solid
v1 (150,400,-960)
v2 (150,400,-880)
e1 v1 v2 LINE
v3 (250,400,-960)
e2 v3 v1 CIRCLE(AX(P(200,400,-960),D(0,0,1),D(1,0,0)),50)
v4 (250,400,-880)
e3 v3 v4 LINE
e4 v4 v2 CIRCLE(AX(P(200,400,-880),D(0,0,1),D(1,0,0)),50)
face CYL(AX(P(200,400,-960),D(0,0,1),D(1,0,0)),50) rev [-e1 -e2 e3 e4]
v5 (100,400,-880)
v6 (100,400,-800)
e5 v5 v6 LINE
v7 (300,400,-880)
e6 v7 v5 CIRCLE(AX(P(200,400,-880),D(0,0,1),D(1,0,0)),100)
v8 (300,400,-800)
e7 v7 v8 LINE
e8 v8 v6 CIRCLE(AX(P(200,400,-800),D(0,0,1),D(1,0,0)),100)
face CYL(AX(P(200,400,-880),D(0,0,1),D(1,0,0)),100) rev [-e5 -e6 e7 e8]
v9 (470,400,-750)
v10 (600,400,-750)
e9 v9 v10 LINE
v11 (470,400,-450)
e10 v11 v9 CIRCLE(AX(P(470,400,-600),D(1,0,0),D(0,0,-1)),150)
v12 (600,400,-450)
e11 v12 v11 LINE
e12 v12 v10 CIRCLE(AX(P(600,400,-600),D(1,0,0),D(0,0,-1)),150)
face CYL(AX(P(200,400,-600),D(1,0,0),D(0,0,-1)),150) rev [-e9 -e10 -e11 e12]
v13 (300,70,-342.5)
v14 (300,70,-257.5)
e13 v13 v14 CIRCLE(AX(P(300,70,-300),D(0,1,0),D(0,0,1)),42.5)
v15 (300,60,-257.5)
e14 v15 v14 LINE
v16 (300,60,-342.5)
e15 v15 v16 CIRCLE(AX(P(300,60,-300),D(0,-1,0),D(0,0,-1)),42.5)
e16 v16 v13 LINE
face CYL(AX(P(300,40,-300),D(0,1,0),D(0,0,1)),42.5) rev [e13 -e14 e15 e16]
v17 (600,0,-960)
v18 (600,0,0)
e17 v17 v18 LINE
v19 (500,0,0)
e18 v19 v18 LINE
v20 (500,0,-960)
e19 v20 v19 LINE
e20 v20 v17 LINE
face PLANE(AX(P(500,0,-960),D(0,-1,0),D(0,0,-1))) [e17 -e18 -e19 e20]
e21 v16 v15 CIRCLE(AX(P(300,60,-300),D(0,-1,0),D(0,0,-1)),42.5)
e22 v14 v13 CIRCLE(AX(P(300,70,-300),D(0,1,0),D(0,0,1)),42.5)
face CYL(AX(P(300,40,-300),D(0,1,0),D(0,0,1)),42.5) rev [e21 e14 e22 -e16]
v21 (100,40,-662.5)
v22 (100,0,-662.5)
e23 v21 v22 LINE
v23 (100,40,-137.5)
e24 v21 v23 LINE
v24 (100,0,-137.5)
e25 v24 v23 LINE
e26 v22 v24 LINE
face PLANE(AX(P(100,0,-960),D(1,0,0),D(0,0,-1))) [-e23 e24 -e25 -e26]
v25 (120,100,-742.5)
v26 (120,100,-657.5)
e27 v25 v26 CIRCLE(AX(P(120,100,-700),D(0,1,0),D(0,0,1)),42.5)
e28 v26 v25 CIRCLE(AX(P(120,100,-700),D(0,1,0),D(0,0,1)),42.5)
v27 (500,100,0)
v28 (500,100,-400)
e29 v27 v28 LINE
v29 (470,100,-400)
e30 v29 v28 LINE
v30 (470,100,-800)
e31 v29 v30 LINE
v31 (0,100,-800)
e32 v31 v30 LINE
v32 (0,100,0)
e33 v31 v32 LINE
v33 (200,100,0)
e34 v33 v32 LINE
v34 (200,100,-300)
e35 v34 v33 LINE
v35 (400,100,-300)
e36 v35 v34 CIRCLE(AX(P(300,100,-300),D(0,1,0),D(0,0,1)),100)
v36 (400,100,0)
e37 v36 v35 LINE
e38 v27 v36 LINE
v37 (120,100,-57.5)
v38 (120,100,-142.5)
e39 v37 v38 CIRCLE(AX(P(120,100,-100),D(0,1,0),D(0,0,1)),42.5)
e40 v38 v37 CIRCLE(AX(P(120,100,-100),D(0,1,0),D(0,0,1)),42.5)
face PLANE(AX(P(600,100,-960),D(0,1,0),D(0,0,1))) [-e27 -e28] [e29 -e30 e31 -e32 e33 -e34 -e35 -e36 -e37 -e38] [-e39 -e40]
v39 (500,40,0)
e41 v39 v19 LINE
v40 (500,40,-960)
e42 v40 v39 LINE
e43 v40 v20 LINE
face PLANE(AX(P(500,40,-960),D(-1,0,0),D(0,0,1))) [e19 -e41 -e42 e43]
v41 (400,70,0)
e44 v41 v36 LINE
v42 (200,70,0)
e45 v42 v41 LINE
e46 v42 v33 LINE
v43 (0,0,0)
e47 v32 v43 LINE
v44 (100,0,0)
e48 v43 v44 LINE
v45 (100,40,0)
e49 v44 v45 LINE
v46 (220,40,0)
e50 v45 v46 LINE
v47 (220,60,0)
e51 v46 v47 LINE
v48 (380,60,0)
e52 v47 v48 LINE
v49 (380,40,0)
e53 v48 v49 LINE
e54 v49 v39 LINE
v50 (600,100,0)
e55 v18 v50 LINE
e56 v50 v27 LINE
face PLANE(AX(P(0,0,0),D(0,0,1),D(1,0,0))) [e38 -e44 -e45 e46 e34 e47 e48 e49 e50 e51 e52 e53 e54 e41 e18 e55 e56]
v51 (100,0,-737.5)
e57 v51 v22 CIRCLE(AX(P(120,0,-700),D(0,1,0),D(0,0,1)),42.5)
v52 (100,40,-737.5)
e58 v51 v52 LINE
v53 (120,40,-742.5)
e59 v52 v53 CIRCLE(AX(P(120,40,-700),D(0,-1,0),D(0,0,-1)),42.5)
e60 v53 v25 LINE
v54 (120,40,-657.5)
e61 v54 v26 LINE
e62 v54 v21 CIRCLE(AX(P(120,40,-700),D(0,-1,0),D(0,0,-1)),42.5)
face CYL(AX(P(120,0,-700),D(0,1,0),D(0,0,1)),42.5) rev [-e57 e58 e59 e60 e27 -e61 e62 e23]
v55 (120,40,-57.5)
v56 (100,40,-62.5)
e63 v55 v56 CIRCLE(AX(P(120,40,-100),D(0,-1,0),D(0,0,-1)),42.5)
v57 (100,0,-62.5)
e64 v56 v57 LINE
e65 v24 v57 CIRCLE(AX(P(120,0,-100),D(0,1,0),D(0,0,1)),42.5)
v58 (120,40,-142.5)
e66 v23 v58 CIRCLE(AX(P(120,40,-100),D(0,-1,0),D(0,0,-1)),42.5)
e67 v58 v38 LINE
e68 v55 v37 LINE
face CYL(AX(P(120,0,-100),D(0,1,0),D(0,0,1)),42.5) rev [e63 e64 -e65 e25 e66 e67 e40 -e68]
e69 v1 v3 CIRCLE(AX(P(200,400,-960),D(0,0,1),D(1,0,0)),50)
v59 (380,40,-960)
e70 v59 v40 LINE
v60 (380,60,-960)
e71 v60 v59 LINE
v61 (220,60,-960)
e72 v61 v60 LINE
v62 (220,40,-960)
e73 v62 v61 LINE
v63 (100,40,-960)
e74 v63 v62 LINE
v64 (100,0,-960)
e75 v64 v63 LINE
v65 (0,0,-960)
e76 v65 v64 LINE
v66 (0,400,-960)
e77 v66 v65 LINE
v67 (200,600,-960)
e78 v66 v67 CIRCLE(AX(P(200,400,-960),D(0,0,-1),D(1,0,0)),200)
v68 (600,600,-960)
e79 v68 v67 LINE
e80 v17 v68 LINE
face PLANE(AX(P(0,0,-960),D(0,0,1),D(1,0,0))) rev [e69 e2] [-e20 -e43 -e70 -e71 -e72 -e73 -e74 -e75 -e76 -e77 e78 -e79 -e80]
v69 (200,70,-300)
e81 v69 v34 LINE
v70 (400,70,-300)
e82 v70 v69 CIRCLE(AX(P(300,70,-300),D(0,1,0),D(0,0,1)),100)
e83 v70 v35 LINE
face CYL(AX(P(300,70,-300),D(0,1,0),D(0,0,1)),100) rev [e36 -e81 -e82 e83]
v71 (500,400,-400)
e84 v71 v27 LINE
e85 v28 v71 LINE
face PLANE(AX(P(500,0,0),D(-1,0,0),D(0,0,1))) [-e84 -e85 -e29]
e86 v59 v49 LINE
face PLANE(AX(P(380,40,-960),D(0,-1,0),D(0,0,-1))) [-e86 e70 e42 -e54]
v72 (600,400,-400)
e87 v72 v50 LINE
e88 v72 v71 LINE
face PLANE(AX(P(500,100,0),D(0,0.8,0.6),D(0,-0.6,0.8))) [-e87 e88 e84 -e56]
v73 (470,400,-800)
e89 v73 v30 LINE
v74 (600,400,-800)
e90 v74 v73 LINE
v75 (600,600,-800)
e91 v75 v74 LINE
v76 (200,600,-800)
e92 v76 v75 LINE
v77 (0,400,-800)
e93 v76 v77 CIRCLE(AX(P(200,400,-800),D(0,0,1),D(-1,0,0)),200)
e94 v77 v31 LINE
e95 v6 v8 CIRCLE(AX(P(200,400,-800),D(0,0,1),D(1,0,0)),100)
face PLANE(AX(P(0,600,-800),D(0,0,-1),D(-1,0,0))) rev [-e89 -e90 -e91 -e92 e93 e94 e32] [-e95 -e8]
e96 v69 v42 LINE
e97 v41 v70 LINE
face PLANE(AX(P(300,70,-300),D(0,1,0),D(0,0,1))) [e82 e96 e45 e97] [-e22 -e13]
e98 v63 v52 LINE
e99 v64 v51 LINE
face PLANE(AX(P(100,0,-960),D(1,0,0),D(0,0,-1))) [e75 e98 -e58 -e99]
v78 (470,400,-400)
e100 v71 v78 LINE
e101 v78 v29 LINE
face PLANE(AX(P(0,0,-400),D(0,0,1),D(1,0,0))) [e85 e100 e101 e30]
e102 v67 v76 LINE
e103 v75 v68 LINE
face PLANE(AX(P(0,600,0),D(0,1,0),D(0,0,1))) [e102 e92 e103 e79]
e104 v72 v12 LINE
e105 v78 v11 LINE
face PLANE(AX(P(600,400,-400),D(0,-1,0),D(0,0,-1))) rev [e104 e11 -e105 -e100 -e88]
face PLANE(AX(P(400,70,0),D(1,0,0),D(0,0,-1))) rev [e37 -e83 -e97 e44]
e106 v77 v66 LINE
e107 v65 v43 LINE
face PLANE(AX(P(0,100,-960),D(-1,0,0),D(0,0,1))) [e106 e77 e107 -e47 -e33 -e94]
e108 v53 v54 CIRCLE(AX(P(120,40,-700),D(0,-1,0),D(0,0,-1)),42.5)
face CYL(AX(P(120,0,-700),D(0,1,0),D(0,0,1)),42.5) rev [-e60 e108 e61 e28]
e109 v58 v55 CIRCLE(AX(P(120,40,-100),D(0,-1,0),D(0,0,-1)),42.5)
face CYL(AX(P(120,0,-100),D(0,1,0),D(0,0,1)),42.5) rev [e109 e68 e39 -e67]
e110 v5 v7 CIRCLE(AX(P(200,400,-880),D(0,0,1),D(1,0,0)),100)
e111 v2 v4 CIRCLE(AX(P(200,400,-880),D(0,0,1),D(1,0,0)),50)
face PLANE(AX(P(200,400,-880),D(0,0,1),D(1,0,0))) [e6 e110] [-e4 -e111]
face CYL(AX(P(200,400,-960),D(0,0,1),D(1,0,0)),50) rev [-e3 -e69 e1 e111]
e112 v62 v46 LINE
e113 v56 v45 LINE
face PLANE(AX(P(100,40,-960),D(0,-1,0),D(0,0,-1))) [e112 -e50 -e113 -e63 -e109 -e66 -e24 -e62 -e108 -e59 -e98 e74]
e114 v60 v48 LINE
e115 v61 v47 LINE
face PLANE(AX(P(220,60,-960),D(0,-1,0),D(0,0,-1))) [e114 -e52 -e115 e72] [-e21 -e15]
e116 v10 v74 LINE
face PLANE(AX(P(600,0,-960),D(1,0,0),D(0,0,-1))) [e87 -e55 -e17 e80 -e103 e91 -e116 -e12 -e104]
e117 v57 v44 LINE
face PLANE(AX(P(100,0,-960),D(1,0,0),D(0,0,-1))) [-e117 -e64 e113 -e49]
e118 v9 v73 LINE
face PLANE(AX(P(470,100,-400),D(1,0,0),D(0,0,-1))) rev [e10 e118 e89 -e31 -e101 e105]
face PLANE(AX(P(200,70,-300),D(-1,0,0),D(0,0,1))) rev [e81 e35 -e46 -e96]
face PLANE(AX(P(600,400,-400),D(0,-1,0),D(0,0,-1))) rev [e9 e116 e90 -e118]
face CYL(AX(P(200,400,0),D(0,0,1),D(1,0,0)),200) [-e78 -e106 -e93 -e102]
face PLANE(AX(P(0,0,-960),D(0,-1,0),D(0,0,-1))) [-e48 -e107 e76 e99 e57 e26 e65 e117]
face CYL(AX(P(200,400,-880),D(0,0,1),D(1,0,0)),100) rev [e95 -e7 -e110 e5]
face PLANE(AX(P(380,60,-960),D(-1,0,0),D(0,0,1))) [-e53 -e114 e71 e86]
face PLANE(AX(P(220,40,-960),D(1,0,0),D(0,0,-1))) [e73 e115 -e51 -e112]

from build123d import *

# Parameters (mm, degrees)
BASE_PLATE_DEPTH            = 960
UPRIGHT_SKETCH_W            = 600
UPRIGHT_SKETCH_H            = 160
UPRIGHT_DEPTH               = 500
UPRIGHT_TOP_ROUND_R200_R    = 200
BORE_COUNTERBORE_SKETCH_R   = 100
BORE_COUNTERBORE_200_DEPTH  = 80
THROUGH_BORE_SKETCH_R       = 50
THROUGH_BORE_100_DEPTH      = 1223.456543195
MOUNTING_HOLES_SKETCH_R     = 42.5
MOUNTING_HOLES_2X_85_DEPTH  = 1238.578280352
BASE_POCKET_30_DEEP_DEPTH   = 30
POCKET_HOLE_SKETCH_R        = 42.5
POCKET_HOLE_85_DEPTH        = 30
FORK_SUPPORT_BLOCK_SKETCH_W = 130
FORK_SUPPORT_BLOCK_SKETCH_H = 300
FORK_SUPPORT_BLOCK_DEPTH    = 400
FORK_CRADLE_SKETCH_R        = 150
FORK_CRADLE_300_DEPTH       = 400
GUSSET_RIB_DEPTH            = 100


with BuildPart() as part:
    # Base Plate Profile Sketch → Base Plate (new body)
    with BuildSketch(Plane.XY):
        Polygon((0, 0), (100, 0), (100, 40), (220, 40), (220, 60), (380, 60), (380, 40), (500, 40), (500, 0), (600, 0), (600, 100), (0, 100), align=None)
    extrude(amount=-BASE_PLATE_DEPTH)

    # Upright Sketch → Upright (add)
    with BuildSketch(Plane(origin=(0, 100, 0), x_dir=(1, 0, 0), z_dir=(0, 1, 0))):
        with Locations((300, 880)):
            Rectangle(UPRIGHT_SKETCH_W, UPRIGHT_SKETCH_H)
    extrude(amount=UPRIGHT_DEPTH)

    # Upright Top Round R200
    upright_top_round_r200_edges = [part.edges().sort_by_distance(p)[0] for p in [
        (0, 600, -880),
    ]]
    fillet(upright_top_round_r200_edges, radius=UPRIGHT_TOP_ROUND_R200_R)

    # Bore Counterbore Sketch → Bore Counterbore Ø200 (cut)
    with BuildSketch(Plane.XY.offset(-800)):
        with Locations((200, 400)):
            Circle(BORE_COUNTERBORE_SKETCH_R)
    extrude(amount=-BORE_COUNTERBORE_200_DEPTH, mode=Mode.SUBTRACT)

    # Through Bore Sketch → Through Bore Ø100 (cut, through all)
    with BuildSketch(Plane.XY.offset(-880)):
        with Locations((200, 400)):
            Circle(THROUGH_BORE_SKETCH_R)
    extrude(amount=-THROUGH_BORE_100_DEPTH, mode=Mode.SUBTRACT)

    # Mounting Holes Sketch → Mounting Holes 2xØ85 (cut, through all)
    with BuildSketch(Plane(origin=(0, 100, 0), x_dir=(1, 0, 0), z_dir=(0, 1, 0))):
        with Locations(Location((120, 700, 0), (0, 0, 270))):
            Circle(MOUNTING_HOLES_SKETCH_R)
        with Locations(Location((120, 100, 0), (0, 0, 270))):
            Circle(MOUNTING_HOLES_SKETCH_R)
    extrude(amount=-MOUNTING_HOLES_2X_85_DEPTH, mode=Mode.SUBTRACT)

    # Base Pocket Sketch → Base Pocket 30 Deep (cut)
    with BuildSketch(Plane(origin=(0, 100, 0), x_dir=(1, 0, 0), z_dir=(0, 1, 0))):
        with BuildLine():
            Line((200, 300), (200, 0))
            Line((200, 0), (400, 0))
            Line((400, 0), (400, 300))
            ThreePointArc((400, 300), (300, 400), (200, 300))
        make_face()
    extrude(amount=-BASE_POCKET_30_DEEP_DEPTH, mode=Mode.SUBTRACT)

    # Pocket Hole Sketch → Pocket Hole Ø85 (cut)
    with BuildSketch(Plane(origin=(0, 70, 0), x_dir=(1, 0, 0), z_dir=(0, 1, 0))):
        with Locations(Location((300, 300, 0), (0, 0, 270))):
            Circle(POCKET_HOLE_SKETCH_R)
    extrude(amount=-POCKET_HOLE_85_DEPTH, mode=Mode.SUBTRACT)

    # Fork Support Block Sketch → Fork Support Block (add)
    with BuildSketch(Plane.XY.offset(-800)):
        with Locations((535, 250)):
            Rectangle(FORK_SUPPORT_BLOCK_SKETCH_W, FORK_SUPPORT_BLOCK_SKETCH_H)
    extrude(amount=FORK_SUPPORT_BLOCK_DEPTH)

    # Fork Cradle Sketch → Fork Cradle Ø300 (cut)
    with BuildSketch(Plane(origin=(600, 0, 0), x_dir=(0, 0, -1), z_dir=(1, 0, 0))):
        with Locations((600, 400)):
            Circle(FORK_CRADLE_SKETCH_R)
    extrude(amount=-FORK_CRADLE_300_DEPTH, mode=Mode.SUBTRACT)

    # Gusset Rib Sketch → Gusset Rib (add)
    with BuildSketch(Plane(origin=(600, 0, 0), x_dir=(0, 0, -1), z_dir=(1, 0, 0))):
        Polygon((400, 400), (400, 100), (0, 100), align=None)
    extrude(amount=-GUSSET_RIB_DEPTH)


solid = part.part
